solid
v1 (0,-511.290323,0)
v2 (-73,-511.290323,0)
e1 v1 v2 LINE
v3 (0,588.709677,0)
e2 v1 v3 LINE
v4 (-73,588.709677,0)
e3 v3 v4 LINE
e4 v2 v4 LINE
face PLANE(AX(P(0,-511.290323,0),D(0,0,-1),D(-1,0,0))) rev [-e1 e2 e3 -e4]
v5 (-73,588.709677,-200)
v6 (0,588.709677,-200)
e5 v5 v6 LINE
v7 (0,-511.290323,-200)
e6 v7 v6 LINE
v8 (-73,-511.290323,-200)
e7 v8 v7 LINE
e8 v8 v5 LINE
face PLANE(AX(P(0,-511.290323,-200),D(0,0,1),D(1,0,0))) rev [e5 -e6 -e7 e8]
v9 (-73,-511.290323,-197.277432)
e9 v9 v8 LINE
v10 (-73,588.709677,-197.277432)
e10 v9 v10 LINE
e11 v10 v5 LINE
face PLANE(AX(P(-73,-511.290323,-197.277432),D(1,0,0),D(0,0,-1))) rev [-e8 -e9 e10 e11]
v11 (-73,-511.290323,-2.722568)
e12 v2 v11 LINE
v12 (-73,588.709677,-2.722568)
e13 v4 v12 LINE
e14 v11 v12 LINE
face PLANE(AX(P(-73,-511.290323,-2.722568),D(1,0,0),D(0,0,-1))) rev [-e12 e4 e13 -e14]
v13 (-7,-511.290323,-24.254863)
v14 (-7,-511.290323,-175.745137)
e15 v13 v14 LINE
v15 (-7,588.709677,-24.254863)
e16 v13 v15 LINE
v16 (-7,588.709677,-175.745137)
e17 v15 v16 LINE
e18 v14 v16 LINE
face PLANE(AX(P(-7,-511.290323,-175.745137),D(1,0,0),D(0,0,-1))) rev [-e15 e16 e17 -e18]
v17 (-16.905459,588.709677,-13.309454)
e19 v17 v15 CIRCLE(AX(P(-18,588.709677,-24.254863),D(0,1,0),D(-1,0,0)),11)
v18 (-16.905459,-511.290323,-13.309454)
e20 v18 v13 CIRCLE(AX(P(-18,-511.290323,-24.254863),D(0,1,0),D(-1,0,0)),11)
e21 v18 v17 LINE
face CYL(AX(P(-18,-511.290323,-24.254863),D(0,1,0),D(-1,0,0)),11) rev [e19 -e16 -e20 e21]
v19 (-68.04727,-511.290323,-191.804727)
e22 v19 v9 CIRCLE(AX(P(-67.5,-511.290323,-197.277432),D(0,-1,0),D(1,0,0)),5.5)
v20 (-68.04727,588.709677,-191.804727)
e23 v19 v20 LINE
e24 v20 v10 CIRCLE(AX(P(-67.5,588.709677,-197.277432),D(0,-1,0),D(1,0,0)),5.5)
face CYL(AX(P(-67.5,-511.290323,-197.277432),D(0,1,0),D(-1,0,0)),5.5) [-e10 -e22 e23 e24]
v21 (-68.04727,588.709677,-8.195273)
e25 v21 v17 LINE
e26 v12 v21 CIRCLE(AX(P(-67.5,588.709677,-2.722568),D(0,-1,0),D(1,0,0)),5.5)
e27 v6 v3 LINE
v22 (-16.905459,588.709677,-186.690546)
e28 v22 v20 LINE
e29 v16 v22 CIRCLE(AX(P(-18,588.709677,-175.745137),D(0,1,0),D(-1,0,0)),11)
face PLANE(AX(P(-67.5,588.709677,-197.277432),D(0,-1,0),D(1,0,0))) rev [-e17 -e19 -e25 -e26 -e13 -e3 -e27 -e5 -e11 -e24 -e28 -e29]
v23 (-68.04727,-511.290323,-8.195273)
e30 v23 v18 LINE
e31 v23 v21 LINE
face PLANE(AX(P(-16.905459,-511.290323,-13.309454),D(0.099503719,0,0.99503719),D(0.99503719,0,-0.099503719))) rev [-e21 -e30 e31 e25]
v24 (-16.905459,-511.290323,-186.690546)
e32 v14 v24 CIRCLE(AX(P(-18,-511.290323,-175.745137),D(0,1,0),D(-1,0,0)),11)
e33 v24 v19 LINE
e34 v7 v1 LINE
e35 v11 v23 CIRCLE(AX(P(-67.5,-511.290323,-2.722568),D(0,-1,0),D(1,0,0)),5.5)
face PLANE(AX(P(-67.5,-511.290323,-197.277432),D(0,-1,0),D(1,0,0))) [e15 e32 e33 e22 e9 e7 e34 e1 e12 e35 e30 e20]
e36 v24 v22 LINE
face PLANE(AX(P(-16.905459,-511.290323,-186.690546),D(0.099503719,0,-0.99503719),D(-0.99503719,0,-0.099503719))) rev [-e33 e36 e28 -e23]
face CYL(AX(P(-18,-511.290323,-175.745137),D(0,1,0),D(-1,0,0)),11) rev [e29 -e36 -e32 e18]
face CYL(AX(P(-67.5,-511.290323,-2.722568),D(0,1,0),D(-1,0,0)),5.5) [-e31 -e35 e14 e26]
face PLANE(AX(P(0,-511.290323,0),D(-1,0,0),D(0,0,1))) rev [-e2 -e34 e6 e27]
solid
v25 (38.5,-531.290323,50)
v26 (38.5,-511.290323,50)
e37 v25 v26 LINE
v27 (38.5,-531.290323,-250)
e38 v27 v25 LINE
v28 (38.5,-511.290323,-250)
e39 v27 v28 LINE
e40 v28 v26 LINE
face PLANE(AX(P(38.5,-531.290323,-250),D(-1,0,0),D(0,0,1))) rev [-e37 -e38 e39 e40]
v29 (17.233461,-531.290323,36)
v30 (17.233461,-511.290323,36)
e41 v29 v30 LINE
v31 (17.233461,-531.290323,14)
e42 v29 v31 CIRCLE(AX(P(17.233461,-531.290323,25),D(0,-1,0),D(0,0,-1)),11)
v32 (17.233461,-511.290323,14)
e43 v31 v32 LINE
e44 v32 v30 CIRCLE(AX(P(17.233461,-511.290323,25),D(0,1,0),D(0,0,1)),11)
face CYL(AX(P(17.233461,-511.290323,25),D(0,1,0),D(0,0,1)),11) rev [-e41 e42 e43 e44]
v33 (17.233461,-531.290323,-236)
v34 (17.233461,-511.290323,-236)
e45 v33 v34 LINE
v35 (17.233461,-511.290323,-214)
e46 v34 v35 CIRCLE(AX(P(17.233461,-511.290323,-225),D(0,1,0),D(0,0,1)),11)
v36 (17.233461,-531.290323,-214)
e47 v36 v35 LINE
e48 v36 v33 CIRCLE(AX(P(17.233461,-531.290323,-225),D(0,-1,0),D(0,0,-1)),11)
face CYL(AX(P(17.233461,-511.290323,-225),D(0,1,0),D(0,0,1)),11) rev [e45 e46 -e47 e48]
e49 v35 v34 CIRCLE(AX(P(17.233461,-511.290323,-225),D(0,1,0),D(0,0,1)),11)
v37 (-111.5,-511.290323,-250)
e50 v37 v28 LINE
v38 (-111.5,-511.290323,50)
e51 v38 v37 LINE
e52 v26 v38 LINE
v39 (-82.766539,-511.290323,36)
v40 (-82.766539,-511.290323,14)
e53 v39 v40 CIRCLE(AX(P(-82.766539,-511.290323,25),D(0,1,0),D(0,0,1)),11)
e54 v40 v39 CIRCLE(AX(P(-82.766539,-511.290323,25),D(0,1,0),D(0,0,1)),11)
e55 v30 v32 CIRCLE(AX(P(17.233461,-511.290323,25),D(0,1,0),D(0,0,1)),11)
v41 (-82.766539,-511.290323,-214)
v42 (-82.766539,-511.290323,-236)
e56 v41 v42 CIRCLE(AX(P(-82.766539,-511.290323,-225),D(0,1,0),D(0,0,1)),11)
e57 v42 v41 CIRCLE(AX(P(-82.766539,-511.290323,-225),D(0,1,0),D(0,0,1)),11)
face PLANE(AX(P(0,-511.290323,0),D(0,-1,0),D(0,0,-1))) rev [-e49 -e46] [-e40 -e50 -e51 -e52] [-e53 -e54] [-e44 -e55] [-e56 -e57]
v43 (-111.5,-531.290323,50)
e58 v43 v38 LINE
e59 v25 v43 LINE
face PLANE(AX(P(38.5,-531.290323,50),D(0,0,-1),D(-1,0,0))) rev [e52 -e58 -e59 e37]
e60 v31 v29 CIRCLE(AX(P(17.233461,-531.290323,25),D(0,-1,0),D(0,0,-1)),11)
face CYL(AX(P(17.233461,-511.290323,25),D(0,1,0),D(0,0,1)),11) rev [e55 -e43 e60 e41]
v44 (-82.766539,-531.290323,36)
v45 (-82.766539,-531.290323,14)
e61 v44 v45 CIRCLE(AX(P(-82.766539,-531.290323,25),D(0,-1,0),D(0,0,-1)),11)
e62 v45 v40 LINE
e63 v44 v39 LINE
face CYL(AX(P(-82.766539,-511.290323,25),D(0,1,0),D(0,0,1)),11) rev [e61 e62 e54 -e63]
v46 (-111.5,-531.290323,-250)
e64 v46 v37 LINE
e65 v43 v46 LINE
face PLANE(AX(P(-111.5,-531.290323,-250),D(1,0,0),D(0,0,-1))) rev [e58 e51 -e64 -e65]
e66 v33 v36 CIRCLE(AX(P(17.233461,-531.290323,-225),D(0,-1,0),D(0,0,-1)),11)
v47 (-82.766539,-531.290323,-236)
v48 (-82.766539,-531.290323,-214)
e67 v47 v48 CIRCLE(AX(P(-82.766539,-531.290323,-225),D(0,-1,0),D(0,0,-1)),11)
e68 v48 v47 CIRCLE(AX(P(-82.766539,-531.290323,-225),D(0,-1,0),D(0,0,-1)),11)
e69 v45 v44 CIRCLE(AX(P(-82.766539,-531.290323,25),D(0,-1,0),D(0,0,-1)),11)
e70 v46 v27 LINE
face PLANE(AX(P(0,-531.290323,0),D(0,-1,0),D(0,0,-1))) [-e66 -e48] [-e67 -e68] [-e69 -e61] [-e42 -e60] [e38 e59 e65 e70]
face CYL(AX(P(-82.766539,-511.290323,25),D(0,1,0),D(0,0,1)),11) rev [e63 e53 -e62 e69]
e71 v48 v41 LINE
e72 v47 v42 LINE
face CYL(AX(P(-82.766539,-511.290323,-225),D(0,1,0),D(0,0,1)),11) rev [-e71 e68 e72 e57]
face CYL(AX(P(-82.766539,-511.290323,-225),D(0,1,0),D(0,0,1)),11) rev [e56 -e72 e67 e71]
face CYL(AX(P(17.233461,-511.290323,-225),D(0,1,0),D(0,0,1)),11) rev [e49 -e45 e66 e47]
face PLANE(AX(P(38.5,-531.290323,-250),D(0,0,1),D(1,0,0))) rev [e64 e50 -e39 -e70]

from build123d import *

# Parameters (mm, degrees)
STRUCTURAL_MEMBER1_DEPTH   = 1100
SKETCH3_W                  = 150
SKETCH3_H                  = 300
BOSS_EXTRUDE1_DEPTH        = 20
SKETCH4_W                  = 11
SKETCH4_H                  = 20.001
F_22_0_22_HOLE1_AT_2_COUNT = 2
F_22_0_22_HOLE1_AT_2_PITCH = 100
MIRROR1_COPY_1_SKETCH_W    = 11
MIRROR1_COPY_1_SKETCH_H    = 20.001


with BuildPart() as part:
    # Sketch1 → Structural Member1 (new body)
    with BuildSketch(Plane.XZ.offset(-588.709677419)):
        with BuildLine():
            Line((0, 0), (0, -200))
            Line((0, -200), (-73, -200))
            Line((-73, -200), (-73, -197.277431592))
            ThreePointArc((-73, -197.277431592), (-71.577988935, -193.586902327), (-68.047270455, -191.804727045))
            Line((-68.047270455, -191.804727045), (-16.905459091, -186.690545909))
            ThreePointArc((-16.905459091, -186.690545909), (-9.844022131, -183.126195345), (-7, -175.745136817))
            Line((-7, -175.745136817), (-7, -24.254863183))
            ThreePointArc((-7, -24.254863183), (-9.844022131, -16.873804655), (-16.905459091, -13.309454091))
            Line((-16.905459091, -13.309454091), (-68.047270455, -8.195272955))
            ThreePointArc((-68.047270455, -8.195272955), (-71.577988935, -6.413097673), (-73, -2.722568408))
            Line((-73, -2.722568408), (-73, 0))
            Line((-73, 0), (0, 0))
        make_face()
    extrude(amount=STRUCTURAL_MEMBER1_DEPTH)


with BuildPart() as body_2:
    # Sketch3 → Boss-Extrude1 (new body)
    with BuildSketch(Plane.XZ.offset(511.290322581)):
        with Locations((-36.5, -100)):
            Rectangle(SKETCH3_W, SKETCH3_H)
    extrude(amount=BOSS_EXTRUDE1_DEPTH)

    # Sketch4 → Ø22.0 (22) Hole1 (revolve, cut)
    with BuildSketch(Plane(origin=(-82.766539474, -511.290322581, -225), x_dir=(0, 0, 1), z_dir=(1, 0, 0))):
        with Locations((5.5, 10.0005)):
            Rectangle(SKETCH4_W, SKETCH4_H)
    f_22_0_22_hole1 = revolve(axis=Axis((-82.766539474, -504.940322581, -225), (0, -1, 0)), mode=Mode.SUBTRACT)

    # Ø22.0 (22) Hole1 at 2: Ø22.0 (22) Hole1 ×2
    with Locations(*[(i * F_22_0_22_HOLE1_AT_2_PITCH, 0, 0) for i in range(1, F_22_0_22_HOLE1_AT_2_COUNT)]):
        add(f_22_0_22_hole1, mode=Mode.SUBTRACT)

    # Mirror1: Ø22.0 (22) Hole1 across plane
    add(f_22_0_22_hole1.mirror(Plane(origin=(0, 0, -100), x_dir=(1, 0, 0), z_dir=(0, 0, -1))), mode=Mode.SUBTRACT)

    # Mirror1 copy 1 sketch → Mirror1 copy 1 (revolve, cut)
    with BuildSketch(Plane(origin=(17.233460526, -511.290322581, 25), x_dir=(0, 0, -1), z_dir=(1, 0, 0))):
        with Locations((5.5, -10.0005)):
            Rectangle(MIRROR1_COPY_1_SKETCH_W, MIRROR1_COPY_1_SKETCH_H)
    revolve(axis=Axis((17.233460526, -504.940322581, 25), (0, 1, 0)), mode=Mode.SUBTRACT)


solid = Compound([part.part, body_2.part])
